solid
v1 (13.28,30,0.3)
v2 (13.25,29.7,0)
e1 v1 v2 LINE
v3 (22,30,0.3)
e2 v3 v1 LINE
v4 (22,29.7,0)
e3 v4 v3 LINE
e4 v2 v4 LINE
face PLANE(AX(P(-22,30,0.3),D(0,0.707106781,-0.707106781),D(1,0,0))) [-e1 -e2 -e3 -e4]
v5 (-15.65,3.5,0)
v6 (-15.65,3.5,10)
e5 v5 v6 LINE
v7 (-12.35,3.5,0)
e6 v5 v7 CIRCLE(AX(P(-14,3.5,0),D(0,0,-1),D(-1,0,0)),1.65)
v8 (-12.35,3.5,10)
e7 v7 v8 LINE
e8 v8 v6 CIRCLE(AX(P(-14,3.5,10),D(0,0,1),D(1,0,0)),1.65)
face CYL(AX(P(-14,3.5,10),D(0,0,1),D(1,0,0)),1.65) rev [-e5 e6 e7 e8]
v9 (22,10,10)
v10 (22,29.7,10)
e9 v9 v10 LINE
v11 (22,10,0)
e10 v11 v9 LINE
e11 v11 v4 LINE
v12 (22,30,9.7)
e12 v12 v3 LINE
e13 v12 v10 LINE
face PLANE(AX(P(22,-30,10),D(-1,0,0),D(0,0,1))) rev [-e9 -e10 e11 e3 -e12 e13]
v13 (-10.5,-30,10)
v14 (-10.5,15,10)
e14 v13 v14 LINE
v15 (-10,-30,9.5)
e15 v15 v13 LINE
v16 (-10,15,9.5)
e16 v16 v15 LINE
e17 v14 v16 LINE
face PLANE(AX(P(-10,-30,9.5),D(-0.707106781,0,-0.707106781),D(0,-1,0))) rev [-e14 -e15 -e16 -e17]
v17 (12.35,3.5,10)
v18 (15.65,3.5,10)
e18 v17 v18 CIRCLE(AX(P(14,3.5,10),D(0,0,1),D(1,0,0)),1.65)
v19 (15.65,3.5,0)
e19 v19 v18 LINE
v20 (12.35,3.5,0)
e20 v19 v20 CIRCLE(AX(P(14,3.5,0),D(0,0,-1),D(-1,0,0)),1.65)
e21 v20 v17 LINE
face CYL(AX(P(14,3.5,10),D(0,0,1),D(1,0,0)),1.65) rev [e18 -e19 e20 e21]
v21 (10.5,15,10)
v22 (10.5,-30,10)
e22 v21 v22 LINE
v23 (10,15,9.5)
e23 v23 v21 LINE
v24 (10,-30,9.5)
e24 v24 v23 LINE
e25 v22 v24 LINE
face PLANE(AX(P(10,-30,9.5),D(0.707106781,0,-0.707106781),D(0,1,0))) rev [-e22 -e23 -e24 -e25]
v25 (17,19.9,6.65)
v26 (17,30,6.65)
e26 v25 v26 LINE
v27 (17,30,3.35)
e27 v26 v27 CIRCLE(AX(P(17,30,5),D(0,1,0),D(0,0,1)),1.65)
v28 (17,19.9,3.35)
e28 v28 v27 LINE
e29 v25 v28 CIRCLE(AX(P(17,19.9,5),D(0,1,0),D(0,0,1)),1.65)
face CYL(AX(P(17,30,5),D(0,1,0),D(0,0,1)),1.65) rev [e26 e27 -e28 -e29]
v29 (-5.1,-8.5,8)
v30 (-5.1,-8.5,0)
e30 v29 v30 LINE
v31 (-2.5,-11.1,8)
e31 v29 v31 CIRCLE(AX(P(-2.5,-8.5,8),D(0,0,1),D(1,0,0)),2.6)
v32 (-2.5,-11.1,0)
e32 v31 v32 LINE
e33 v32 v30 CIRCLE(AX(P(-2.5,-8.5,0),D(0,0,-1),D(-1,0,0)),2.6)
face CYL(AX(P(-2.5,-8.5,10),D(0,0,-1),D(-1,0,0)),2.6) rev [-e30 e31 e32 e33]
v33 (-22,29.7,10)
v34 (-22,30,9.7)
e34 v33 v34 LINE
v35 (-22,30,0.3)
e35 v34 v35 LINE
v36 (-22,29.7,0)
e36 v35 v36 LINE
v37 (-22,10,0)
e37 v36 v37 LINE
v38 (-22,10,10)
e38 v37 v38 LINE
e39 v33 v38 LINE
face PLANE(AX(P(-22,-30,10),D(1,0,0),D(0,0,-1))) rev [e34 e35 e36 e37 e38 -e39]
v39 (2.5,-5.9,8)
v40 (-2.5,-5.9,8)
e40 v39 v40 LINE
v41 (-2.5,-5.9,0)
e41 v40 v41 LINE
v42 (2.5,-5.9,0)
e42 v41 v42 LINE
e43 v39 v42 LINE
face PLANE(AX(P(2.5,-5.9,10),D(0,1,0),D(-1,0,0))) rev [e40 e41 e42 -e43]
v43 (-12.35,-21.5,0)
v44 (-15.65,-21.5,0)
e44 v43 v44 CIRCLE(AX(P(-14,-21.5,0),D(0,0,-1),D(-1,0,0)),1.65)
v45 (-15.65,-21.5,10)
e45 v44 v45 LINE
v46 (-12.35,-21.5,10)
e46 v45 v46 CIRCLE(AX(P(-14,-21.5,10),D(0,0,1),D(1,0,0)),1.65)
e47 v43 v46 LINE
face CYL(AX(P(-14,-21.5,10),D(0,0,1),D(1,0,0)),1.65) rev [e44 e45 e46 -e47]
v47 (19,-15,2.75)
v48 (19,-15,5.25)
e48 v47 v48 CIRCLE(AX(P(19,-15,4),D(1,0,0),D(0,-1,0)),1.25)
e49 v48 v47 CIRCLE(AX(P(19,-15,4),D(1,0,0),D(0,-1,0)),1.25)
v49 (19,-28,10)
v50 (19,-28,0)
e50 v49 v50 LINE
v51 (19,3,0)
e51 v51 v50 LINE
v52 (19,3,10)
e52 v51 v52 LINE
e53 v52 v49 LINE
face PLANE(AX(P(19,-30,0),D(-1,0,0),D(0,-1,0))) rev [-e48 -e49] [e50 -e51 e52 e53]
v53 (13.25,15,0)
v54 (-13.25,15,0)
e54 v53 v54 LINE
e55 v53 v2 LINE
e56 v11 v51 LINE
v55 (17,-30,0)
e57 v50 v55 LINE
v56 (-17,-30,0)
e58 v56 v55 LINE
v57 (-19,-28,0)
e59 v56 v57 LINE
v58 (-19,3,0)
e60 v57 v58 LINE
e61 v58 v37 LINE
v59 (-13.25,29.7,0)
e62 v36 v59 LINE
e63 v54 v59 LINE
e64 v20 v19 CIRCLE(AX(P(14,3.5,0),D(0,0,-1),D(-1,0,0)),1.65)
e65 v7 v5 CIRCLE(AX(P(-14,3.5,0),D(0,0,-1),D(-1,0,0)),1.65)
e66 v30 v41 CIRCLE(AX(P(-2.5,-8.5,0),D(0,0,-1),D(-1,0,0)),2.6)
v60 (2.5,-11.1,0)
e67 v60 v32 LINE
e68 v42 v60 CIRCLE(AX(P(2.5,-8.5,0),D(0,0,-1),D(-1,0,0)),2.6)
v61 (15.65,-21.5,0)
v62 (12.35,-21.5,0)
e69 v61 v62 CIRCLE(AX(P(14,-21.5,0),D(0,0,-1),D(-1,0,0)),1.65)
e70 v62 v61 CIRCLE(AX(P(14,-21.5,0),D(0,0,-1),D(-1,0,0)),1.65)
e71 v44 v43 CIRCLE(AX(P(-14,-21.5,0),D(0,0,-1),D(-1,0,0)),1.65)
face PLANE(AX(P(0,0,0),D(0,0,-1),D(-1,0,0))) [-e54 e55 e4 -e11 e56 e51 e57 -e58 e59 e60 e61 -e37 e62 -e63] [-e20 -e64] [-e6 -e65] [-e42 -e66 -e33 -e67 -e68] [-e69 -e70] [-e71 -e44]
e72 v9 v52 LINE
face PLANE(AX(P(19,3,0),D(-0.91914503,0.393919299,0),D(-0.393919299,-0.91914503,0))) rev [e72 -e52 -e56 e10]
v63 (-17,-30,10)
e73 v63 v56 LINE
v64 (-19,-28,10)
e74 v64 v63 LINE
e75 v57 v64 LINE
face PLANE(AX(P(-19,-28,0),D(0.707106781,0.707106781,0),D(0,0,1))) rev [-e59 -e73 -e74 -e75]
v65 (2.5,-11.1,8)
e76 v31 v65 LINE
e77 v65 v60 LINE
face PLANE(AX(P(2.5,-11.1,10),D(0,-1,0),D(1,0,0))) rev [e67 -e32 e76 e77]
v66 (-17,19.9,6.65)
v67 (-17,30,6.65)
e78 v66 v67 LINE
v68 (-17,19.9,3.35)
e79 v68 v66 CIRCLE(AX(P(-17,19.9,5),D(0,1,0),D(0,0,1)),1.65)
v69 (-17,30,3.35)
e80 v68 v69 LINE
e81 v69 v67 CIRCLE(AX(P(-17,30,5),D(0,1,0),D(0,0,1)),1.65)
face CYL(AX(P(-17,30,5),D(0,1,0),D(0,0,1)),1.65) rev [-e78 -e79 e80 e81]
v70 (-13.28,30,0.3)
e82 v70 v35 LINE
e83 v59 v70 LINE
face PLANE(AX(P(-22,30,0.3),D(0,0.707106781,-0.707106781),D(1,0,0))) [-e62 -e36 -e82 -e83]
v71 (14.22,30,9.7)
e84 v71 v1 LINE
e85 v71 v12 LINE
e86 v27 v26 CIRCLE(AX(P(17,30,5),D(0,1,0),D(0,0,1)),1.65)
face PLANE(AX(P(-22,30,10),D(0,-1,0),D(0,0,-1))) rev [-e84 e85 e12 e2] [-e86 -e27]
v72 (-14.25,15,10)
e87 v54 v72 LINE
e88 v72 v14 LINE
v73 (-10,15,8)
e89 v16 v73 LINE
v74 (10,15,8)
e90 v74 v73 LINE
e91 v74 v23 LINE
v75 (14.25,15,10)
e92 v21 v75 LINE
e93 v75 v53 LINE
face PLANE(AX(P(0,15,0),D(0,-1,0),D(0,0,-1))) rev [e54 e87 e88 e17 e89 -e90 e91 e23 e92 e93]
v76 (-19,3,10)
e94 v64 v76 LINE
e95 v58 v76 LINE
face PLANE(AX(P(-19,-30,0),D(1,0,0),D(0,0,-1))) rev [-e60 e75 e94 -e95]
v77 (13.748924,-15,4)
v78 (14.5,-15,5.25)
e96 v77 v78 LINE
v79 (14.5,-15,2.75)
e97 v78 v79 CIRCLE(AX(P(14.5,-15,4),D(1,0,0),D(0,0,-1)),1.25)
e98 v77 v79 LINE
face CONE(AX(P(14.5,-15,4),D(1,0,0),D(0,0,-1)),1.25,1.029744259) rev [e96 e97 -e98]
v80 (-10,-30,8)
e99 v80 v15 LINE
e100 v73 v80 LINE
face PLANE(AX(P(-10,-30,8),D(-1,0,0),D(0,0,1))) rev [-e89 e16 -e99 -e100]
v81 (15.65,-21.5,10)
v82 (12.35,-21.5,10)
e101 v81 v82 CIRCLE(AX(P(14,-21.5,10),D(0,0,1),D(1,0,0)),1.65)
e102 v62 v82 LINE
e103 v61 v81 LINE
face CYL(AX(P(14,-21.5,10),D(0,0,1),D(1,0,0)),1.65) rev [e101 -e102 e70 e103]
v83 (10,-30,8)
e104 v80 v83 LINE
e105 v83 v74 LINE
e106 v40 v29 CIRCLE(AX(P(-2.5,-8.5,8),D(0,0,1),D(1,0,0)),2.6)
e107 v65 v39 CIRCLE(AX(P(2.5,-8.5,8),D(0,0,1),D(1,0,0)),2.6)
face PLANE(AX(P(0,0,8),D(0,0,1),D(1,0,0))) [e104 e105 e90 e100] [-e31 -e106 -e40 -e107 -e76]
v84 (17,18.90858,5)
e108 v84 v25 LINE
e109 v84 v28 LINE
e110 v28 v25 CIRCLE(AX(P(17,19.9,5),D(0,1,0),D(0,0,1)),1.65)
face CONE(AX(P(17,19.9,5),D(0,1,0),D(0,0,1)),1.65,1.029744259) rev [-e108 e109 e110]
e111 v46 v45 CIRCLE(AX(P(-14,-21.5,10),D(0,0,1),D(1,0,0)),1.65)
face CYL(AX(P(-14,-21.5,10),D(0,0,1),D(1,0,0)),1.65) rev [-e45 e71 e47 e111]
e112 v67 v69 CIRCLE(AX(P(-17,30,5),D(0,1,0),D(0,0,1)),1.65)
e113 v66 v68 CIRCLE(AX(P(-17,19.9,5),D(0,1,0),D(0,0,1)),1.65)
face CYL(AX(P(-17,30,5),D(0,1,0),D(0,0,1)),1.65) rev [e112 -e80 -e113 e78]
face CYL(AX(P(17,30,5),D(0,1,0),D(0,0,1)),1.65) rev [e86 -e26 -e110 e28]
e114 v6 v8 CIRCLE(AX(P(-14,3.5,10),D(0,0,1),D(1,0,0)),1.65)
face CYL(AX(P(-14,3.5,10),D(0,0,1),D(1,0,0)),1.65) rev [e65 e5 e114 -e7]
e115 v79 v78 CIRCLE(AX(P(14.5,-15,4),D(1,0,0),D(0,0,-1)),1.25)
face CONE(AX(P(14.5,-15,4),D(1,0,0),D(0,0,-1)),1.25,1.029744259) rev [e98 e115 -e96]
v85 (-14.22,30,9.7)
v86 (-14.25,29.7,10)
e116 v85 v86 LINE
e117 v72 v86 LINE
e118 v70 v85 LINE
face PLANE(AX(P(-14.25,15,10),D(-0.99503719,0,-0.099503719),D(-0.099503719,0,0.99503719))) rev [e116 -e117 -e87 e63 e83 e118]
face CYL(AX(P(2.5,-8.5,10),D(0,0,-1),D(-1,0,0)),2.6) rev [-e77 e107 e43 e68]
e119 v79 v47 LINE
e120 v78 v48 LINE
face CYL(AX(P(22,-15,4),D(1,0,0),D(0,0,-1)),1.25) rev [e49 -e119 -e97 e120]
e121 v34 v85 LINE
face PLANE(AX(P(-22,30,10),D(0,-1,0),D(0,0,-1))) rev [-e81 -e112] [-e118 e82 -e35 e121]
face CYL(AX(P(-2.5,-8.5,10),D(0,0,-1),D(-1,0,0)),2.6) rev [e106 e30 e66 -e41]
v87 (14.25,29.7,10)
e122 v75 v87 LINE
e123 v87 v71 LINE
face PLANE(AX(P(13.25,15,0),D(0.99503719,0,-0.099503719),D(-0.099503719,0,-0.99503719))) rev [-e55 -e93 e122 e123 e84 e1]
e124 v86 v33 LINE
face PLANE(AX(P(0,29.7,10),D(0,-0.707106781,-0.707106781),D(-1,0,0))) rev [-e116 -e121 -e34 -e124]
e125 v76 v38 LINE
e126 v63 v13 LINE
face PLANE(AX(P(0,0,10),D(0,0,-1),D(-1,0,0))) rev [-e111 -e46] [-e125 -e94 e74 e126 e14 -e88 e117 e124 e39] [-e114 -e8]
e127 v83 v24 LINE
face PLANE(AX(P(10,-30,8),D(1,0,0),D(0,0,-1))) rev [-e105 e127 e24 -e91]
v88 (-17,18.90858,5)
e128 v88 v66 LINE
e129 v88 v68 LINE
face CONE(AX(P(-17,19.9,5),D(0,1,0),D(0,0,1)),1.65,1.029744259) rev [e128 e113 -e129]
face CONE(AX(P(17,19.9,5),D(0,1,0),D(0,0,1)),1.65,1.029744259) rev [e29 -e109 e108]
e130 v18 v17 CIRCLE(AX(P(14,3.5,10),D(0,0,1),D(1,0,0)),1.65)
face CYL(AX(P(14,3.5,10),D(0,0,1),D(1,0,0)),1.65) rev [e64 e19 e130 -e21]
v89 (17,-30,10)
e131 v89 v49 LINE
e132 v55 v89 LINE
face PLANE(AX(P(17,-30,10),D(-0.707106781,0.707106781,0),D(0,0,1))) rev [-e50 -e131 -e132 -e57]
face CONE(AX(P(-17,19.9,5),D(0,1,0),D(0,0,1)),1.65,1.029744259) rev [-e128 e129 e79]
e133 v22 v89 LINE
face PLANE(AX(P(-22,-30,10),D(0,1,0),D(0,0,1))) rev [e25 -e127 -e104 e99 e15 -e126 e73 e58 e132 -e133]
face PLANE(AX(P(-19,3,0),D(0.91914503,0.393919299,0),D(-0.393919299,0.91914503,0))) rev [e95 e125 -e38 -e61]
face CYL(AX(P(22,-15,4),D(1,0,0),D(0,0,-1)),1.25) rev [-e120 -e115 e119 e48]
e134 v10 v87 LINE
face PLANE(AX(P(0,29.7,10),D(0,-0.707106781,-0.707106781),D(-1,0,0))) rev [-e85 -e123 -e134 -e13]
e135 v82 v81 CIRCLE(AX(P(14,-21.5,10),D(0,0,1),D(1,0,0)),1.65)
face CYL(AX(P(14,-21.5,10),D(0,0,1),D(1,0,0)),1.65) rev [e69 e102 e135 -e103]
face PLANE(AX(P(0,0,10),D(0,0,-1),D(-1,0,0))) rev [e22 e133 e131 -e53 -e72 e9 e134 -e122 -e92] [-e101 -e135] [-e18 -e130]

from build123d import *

# Parameters (mm, degrees)
SKETCH1_W             = 44
SKETCH1_H             = 60
BOSS_EXTRUDE1_DEPTH   = 10
CUT_EXTRUDE4_DEPTH    = 15
SKETCH2_W             = 20
SKETCH2_H             = 60
CUT_EXTRUDE1_DEPTH    = 2
M4_TAPPED_HOLE1_D     = 3.3
M4_TAPPED_HOLE1_DEPTH = 10.1
M4_TAPPED_HOLE1_TIP   = 0.991420021
M4_TAPPED_HOLE2_D     = 3.3
M4_TAPPED_HOLE2_DEPTH = 10.1
M4_TAPPED_HOLE2_TIP   = 0.991420021
M3_TAPPED_HOLE2_D     = 2.5
M3_TAPPED_HOLE2_DEPTH = 7.5
M3_TAPPED_HOLE2_TIP   = 0.751075774
CHAMFER3_SIZE         = 0.3
CHAMFER4_SIZE         = 0.5
CUT_EXTRUDE5_DEPTH    = 39.522720569
CHAMFER5_SIZE         = 2
CUT_EXTRUDE6_DEPTH    = 39.522720569


with BuildPart() as part:
    # Sketch1 → Boss-Extrude1 (new body)
    with BuildSketch(Plane.XY):
        Rectangle(SKETCH1_W, SKETCH1_H)
    extrude(amount=BOSS_EXTRUDE1_DEPTH)

    # Sketch13 → Cut-Extrude4 (cut)
    with BuildSketch(Plane(origin=(0, 30, 0), x_dir=(1, 0, 0), z_dir=(0, 1, 0))):
        Polygon((13.25, 0), (14.25, -10), (-14.25, -10), (-13.25, 0), align=None)
    extrude(amount=-CUT_EXTRUDE4_DEPTH, mode=Mode.SUBTRACT)

    # Sketch2 → Cut-Extrude1 (cut)
    with BuildSketch(Plane.XY.offset(10)):
        Rectangle(SKETCH2_W, SKETCH2_H)
    extrude(amount=-CUT_EXTRUDE1_DEPTH, mode=Mode.SUBTRACT)

    # M4 Tapped Hole1
    with Locations(Plane(origin=(0, 30, 0), x_dir=(1, 0, 0), z_dir=(0, 1, 0))):
        with Locations((-17, -5), (17, -5)):
            Hole(M4_TAPPED_HOLE1_D / 2, depth=M4_TAPPED_HOLE1_DEPTH)
            with Locations((0, 0, -(M4_TAPPED_HOLE1_DEPTH + M4_TAPPED_HOLE1_TIP / 2))):  # 118° drill point
                Cone(0, M4_TAPPED_HOLE1_D / 2, M4_TAPPED_HOLE1_TIP, mode=Mode.SUBTRACT)

    # M4 Tapped Hole2
    with Locations(Plane.XY.offset(10)):
        with Locations((-14, -21.5), (14, -21.5), (-14, 3.5), (14, 3.5)):
            Hole(M4_TAPPED_HOLE2_D / 2, depth=M4_TAPPED_HOLE2_DEPTH)
            with Locations((0, 0, -(M4_TAPPED_HOLE2_DEPTH + M4_TAPPED_HOLE2_TIP / 2))):  # 118° drill point
                Cone(0, M4_TAPPED_HOLE2_D / 2, M4_TAPPED_HOLE2_TIP, mode=Mode.SUBTRACT)

    # M3 Tapped Hole2
    with Locations(Plane(origin=(22, 0, 0), x_dir=(0, 0, -1), z_dir=(1, 0, 0))):
        with Locations((-4, -15)):
            Hole(M3_TAPPED_HOLE2_D / 2, depth=M3_TAPPED_HOLE2_DEPTH)
            with Locations((0, 0, -(M3_TAPPED_HOLE2_DEPTH + M3_TAPPED_HOLE2_TIP / 2))):  # 118° drill point
                Cone(0, M3_TAPPED_HOLE2_D / 2, M3_TAPPED_HOLE2_TIP, mode=Mode.SUBTRACT)

    # Chamfer3
    chamfer3_edges = [part.edges().sort_by_distance(p)[0] for p in [
        (-17.625, 30, 0),
        (-18.125, 30, 10),
        (17.625, 30, 0),
        (18.125, 30, 10),
    ]]
    chamfer(chamfer3_edges, length=CHAMFER3_SIZE)

    # Chamfer4
    chamfer4_edges = [part.edges().sort_by_distance(p)[0] for p in [
        (10, -7.5, 10),
        (-10, -7.5, 10),
    ]]
    chamfer(chamfer4_edges, length=CHAMFER4_SIZE)

    # Sketch14 → Cut-Extrude5 (cut, through all)
    with BuildSketch(Plane.XY.offset(10)):
        Polygon((-19, -30), (-19, 3), (-22, 10), (-22, -30), align=None)
        Polygon((19, -30), (19, 3), (22, 10), (22, -30), align=None)
    extrude(amount=-CUT_EXTRUDE5_DEPTH, mode=Mode.SUBTRACT)

    # Chamfer5
    chamfer5_edges = [part.edges().sort_by_distance(p)[0] for p in [
        (-19, -30, 5),
        (19, -30, 5),
    ]]
    chamfer(chamfer5_edges, length=CHAMFER5_SIZE)

    # Sketch15 → Cut-Extrude6 (cut, through all)
    with BuildSketch(Plane(origin=(0, 0, 0), x_dir=(-1, 0, 0), z_dir=(0, 0, -1))):
        with BuildLine():
            Line((-2.5, -5.9), (2.5, -5.9))
            ThreePointArc((2.5, -5.9), (5.1, -8.5), (2.5, -11.1))
            Line((2.5, -11.1), (-2.5, -11.1))
            ThreePointArc((-2.5, -11.1), (-5.1, -8.5), (-2.5, -5.9))
        make_face()
    extrude(amount=-CUT_EXTRUDE6_DEPTH, mode=Mode.SUBTRACT)


solid = part.part
